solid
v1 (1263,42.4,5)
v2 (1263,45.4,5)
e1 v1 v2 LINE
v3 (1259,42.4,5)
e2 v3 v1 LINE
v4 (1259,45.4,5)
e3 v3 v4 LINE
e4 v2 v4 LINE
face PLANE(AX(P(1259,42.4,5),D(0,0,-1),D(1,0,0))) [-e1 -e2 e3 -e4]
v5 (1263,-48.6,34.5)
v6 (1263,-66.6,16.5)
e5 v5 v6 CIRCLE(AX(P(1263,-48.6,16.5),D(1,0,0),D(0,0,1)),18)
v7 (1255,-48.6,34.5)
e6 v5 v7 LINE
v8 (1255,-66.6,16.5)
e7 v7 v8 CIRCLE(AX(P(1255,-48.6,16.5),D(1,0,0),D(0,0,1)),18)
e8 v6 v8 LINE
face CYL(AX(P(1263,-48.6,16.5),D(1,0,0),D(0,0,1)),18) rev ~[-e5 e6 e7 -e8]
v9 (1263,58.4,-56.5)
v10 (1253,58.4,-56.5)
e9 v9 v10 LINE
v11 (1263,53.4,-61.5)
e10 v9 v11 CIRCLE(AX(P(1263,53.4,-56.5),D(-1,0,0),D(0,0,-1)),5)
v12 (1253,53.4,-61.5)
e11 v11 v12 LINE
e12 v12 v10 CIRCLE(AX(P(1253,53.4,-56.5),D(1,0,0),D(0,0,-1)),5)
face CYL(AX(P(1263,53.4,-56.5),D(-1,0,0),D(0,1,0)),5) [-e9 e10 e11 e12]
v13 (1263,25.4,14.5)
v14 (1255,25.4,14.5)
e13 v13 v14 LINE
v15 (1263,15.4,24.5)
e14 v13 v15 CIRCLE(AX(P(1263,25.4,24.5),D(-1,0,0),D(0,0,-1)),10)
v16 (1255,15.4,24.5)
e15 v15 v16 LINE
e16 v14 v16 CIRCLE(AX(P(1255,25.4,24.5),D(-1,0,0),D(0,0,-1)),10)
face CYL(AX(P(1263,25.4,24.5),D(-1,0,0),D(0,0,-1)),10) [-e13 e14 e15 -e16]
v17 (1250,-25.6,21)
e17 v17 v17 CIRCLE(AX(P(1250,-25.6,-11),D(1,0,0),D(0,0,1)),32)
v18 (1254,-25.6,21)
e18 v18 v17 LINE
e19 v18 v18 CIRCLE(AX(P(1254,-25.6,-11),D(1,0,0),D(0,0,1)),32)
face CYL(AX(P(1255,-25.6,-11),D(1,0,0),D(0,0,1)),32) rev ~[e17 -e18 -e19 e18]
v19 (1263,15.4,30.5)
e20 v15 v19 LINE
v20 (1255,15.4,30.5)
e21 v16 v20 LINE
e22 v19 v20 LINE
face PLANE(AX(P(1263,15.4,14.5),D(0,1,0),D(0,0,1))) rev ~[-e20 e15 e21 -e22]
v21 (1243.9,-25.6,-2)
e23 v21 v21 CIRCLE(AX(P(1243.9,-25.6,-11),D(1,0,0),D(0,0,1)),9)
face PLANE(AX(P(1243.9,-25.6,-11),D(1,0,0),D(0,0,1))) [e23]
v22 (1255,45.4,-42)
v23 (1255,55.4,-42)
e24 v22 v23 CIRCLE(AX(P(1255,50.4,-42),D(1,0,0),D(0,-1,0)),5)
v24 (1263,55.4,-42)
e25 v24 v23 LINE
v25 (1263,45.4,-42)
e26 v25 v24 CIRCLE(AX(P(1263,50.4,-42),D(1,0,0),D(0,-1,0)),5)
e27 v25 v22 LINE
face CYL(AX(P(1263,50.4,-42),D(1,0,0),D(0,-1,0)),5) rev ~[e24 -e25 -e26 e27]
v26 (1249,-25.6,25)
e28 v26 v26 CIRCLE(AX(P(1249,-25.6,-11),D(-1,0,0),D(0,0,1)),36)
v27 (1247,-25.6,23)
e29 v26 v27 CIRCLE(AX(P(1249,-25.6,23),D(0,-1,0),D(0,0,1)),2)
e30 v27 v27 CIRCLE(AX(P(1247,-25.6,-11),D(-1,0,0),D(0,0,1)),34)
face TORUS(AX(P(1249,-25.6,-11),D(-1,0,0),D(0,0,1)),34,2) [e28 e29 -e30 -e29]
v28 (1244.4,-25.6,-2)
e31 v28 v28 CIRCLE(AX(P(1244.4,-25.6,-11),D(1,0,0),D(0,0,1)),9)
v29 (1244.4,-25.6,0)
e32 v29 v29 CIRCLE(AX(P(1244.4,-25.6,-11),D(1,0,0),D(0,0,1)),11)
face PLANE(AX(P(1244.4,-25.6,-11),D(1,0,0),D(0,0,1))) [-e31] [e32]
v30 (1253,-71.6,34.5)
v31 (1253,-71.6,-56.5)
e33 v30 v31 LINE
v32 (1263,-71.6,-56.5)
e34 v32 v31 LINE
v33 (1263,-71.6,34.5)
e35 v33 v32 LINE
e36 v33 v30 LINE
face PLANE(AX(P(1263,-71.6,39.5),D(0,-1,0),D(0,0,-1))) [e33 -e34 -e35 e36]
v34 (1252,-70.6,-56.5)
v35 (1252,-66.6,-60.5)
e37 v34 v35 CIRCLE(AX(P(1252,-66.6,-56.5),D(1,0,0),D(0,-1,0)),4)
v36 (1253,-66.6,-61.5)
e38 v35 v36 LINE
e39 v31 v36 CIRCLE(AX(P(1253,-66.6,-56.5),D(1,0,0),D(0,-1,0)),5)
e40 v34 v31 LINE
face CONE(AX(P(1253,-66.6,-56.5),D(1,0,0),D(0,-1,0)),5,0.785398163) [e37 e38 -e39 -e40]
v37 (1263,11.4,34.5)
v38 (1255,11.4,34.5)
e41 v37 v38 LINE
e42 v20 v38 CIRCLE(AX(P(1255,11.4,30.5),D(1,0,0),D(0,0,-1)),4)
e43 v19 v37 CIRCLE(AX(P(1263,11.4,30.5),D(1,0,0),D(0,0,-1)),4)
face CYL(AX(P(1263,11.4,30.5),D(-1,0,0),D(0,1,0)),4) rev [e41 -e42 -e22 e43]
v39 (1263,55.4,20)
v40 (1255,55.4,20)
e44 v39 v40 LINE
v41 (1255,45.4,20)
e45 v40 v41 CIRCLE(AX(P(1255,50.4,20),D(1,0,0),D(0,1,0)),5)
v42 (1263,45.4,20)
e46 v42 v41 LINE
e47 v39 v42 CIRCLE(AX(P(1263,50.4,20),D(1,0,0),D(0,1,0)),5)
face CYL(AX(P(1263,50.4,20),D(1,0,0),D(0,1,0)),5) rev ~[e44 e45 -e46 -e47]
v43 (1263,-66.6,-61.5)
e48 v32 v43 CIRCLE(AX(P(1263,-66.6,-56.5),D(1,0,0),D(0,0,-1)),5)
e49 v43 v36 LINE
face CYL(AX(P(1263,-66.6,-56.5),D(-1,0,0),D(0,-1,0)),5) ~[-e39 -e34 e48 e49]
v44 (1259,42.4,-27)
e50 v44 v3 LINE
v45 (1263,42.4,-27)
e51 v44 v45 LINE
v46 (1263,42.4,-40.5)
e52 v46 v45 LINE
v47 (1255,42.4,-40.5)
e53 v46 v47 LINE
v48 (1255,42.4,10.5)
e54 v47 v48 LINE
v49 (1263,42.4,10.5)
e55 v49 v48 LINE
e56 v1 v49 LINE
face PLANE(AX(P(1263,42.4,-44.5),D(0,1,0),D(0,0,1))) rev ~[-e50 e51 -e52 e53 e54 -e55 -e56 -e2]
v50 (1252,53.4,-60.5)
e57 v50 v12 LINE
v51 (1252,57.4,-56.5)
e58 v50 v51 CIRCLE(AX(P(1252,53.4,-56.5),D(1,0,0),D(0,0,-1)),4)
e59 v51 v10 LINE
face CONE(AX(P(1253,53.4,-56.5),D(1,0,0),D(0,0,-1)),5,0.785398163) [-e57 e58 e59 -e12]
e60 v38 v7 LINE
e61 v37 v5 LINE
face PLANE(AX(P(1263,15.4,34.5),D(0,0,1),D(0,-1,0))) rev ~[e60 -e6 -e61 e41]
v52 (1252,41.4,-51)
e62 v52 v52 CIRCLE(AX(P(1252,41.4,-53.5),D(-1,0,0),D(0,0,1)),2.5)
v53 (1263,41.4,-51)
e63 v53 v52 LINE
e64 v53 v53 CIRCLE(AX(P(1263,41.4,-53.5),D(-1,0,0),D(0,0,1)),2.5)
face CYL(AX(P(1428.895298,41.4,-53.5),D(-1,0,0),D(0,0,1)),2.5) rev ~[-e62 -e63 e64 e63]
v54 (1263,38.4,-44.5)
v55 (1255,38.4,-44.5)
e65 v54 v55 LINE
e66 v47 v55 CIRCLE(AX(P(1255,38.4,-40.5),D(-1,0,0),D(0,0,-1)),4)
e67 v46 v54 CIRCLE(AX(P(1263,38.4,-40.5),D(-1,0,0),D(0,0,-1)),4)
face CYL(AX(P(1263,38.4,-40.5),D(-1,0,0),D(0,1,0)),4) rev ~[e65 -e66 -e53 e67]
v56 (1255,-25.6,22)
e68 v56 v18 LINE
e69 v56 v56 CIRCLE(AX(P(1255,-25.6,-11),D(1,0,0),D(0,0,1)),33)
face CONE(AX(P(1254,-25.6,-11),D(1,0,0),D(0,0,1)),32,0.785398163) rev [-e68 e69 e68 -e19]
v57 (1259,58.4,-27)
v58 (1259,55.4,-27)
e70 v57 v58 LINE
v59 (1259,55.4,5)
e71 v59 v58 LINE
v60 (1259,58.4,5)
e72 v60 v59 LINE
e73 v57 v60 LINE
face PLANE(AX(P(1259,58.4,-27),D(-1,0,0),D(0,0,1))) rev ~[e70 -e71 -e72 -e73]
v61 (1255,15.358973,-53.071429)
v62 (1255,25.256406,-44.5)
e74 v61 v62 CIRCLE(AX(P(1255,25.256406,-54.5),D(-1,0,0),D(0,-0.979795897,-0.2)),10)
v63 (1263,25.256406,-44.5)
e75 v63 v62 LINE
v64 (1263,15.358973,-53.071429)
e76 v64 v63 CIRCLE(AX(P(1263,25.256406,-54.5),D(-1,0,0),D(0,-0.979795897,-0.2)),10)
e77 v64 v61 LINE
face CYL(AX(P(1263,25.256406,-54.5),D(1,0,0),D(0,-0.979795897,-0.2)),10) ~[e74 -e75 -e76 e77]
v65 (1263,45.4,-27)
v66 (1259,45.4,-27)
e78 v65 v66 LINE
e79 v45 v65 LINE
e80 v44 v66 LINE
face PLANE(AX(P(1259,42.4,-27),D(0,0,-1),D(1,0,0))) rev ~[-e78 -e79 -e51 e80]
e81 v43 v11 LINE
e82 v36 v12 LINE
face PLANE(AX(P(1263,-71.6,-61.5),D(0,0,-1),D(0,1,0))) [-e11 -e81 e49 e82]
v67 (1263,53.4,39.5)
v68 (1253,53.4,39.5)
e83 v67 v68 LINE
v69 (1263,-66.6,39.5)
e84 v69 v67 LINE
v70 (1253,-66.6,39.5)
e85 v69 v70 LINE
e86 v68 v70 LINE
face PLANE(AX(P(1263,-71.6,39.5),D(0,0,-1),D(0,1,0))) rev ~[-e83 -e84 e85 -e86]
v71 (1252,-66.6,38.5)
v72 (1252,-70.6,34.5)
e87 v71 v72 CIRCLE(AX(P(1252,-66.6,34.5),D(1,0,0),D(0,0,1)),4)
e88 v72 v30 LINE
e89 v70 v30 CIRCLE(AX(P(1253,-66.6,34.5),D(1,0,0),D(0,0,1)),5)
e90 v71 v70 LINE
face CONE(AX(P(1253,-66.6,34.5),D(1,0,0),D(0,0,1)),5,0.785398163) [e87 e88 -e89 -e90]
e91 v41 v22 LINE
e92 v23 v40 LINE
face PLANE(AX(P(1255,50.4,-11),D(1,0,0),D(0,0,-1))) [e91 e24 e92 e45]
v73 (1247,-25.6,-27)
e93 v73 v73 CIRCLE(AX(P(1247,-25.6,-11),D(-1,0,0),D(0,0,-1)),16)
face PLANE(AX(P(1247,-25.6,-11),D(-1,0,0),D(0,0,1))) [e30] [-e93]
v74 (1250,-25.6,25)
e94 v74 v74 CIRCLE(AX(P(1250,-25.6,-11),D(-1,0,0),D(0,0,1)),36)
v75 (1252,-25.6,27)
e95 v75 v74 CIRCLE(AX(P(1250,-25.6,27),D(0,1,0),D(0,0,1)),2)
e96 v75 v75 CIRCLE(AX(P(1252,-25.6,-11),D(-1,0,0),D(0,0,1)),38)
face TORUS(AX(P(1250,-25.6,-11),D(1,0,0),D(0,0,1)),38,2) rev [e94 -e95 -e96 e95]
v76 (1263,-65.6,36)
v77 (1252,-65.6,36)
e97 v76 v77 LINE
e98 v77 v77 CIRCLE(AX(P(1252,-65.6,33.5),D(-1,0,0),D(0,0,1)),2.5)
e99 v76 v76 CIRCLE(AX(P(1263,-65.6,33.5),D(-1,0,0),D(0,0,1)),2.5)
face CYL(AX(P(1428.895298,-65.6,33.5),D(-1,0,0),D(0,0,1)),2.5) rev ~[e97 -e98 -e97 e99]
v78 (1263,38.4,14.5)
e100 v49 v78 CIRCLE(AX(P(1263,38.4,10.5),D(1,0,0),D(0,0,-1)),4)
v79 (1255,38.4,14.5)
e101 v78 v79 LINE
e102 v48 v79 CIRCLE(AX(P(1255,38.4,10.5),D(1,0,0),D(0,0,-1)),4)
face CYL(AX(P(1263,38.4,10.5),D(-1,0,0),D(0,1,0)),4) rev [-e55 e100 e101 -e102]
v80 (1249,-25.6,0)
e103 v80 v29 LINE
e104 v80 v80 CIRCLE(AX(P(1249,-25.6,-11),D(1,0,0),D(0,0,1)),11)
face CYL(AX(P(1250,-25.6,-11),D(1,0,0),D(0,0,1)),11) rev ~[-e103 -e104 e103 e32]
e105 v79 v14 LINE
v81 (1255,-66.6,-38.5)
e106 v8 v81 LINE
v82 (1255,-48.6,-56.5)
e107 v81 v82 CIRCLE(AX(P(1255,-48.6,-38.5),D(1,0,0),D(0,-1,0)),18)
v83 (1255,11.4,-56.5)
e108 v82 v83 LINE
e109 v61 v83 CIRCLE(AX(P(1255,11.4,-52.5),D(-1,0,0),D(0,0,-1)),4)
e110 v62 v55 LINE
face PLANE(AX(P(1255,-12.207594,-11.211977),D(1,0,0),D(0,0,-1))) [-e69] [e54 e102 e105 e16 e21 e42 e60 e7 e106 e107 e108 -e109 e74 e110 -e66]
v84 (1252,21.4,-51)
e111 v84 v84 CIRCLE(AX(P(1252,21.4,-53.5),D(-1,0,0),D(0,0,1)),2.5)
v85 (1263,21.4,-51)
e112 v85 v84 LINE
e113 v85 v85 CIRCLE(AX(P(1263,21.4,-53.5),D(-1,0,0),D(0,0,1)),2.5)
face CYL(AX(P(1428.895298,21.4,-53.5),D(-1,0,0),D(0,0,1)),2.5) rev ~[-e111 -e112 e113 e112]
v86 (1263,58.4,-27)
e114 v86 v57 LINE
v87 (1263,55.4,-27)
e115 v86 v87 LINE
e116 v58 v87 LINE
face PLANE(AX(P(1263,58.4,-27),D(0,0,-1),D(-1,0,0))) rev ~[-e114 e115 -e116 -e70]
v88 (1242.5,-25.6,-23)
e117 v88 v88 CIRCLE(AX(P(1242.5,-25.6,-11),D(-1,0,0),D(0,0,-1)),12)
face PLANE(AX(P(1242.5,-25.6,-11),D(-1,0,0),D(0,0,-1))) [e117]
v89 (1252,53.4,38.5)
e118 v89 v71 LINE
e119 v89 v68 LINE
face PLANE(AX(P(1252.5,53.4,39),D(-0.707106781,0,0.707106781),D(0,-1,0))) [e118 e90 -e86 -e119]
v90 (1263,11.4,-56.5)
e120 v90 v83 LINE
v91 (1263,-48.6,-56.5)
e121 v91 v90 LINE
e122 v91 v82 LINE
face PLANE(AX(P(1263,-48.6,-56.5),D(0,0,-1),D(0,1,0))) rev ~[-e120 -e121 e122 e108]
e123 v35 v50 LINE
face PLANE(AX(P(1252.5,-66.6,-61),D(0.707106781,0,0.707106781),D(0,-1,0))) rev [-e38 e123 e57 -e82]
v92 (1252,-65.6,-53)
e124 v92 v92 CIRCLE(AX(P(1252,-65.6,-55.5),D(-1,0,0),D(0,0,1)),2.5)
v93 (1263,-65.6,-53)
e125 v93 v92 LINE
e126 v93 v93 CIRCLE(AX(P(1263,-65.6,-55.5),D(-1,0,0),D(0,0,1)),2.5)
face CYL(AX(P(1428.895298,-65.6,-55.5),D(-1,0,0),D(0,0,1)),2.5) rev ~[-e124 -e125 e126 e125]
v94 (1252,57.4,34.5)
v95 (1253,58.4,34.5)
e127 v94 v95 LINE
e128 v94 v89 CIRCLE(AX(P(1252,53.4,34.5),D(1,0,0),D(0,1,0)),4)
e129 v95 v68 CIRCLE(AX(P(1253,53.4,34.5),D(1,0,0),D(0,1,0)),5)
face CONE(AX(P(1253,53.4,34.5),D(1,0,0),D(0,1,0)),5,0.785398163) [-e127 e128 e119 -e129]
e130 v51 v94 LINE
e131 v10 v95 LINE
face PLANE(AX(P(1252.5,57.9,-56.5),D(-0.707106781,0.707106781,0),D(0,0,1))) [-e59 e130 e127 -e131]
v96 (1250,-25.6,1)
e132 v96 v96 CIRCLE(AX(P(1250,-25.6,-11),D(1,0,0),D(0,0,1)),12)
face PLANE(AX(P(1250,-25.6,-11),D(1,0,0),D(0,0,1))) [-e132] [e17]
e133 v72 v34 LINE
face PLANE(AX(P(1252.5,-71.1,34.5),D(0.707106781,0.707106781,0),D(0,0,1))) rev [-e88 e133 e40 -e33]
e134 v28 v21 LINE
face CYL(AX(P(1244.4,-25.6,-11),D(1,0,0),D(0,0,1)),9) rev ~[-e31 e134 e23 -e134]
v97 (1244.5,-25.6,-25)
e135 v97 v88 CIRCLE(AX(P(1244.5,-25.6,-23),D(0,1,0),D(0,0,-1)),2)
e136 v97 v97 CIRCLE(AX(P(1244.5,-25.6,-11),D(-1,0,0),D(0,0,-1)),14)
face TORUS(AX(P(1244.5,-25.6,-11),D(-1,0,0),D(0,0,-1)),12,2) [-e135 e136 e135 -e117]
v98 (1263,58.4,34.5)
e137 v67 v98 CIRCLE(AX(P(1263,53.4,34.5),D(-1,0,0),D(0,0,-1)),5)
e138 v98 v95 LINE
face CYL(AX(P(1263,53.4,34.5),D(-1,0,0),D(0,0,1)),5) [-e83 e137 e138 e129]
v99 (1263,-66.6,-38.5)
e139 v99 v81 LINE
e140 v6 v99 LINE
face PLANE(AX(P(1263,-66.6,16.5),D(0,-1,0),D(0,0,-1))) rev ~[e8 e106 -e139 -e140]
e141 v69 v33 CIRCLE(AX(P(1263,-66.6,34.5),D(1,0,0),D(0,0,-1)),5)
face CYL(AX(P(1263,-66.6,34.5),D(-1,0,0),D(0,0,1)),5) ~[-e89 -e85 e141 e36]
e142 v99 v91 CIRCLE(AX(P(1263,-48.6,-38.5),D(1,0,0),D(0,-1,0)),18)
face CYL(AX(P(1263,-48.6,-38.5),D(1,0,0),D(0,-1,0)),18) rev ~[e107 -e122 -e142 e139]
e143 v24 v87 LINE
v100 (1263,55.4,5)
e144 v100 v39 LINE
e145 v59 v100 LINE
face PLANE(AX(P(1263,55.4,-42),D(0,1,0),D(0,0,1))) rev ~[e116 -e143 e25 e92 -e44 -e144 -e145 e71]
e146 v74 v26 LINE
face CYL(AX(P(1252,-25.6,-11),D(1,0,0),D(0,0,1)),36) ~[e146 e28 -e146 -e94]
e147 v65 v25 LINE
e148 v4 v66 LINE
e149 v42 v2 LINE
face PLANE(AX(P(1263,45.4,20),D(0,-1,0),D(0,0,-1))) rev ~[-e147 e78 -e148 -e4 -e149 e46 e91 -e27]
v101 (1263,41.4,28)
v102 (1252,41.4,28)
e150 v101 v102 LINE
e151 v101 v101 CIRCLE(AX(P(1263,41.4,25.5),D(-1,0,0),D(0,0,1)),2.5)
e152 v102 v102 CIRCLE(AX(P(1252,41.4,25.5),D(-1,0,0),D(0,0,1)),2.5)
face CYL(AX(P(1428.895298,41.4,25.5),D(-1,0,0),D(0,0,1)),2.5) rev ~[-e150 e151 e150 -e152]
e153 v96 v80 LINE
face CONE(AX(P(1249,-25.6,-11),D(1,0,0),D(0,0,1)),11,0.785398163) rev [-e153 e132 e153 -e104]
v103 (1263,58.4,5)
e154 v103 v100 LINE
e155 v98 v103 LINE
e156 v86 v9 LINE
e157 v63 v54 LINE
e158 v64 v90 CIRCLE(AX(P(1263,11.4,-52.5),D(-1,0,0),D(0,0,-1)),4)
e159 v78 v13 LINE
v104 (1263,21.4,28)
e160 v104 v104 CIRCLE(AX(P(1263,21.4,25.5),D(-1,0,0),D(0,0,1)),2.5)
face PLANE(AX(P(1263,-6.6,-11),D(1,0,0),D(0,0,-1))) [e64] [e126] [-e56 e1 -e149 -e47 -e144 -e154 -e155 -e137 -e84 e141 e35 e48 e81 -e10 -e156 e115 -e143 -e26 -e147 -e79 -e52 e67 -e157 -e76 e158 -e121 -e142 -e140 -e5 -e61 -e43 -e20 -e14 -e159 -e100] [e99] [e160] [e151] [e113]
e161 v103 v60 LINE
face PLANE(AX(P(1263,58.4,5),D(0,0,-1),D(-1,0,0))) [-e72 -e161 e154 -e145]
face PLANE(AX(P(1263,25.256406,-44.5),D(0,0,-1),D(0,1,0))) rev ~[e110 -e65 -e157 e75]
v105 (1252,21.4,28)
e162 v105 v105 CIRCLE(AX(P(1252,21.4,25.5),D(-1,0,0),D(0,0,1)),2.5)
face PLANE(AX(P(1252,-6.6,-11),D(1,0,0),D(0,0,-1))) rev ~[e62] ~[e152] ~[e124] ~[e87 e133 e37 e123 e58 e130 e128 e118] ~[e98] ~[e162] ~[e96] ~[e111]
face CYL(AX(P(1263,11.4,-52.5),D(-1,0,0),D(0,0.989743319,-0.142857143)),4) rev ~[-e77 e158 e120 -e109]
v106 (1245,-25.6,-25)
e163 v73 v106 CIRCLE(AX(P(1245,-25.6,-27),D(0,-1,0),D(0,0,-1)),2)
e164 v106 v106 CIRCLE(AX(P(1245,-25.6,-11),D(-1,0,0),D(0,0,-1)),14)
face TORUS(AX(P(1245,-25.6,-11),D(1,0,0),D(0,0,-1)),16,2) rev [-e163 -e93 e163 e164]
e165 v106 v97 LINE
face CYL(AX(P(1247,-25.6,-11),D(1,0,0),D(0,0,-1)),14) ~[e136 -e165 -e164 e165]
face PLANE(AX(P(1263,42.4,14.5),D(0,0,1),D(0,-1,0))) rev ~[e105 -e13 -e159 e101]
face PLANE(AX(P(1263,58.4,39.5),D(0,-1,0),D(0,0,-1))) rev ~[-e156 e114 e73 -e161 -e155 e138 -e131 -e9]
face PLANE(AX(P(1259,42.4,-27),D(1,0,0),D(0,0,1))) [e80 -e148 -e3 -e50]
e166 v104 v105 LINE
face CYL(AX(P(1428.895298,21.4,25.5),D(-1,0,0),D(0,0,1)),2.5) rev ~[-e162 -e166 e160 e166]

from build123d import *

# Parameters (mm, degrees)
SKETCH_1_W          = 101
SKETCH_1_H          = 130
EXTRUDE_1_DEPTH     = 11
CUT_EXTRUDE_1_DEPTH = 8
CUT_EXTRUDE_2_DEPTH = 8
CUT_EXTRUDE_3_REACH = 1271.625
SKETCH_4_W          = 4
SKETCH_4_H          = 32
CUT_EXTRUDE_4_REACH = 1273.161
SKETCH_5_W          = 4
SKETCH_5_H          = 32
SKETCH_6_R          = 36
EXTRUDE_2_DEPTH     = 5
SKETCH_7_R          = 14
EXTRUDE_3_DEPTH     = 4.5
SKETCH_8_R          = 32
CUT_EXTRUDE_5_DEPTH = 5
SKETCH_9_R          = 11
CUT_EXTRUDE_6_DEPTH = 5.6
SKETCH_10_R         = 9
CUT_EXTRUDE_7_DEPTH = 0.5
HOLE_WIZARD_M6_1_D  = 5
FILLET_1_R          = 5
CHAMFER_1_SIZE      = 1
FILLET_2_R          = 2
FILLET_3_R          = 4
FILLET_4_R          = 10


with BuildPart() as part:
    # 草图1 → 凸台-拉伸1 (new body)
    with BuildSketch(Plane(origin=(1263, 0, 0), x_dir=(0, 0, -1), z_dir=(1, 0, 0))):
        with Locations((11, -6.6)):
            Rectangle(SKETCH_1_W, SKETCH_1_H)
    extrude(amount=-EXTRUDE_1_DEPTH)

    # 草图2 → 切除-拉伸1 (cut)
    with BuildSketch(Plane(origin=(1263, 0, 0), x_dir=(0, 0, -1), z_dir=(1, 0, 0))):
        with BuildLine():
            Line((44.5, 25.256406461), (44.5, 42.4))
            Line((44.5, 42.4), (-14.5, 42.4))
            Line((-14.5, 42.4), (-14.5, 15.4))
            Line((-14.5, 15.4), (-34.5, 15.4))
            Line((-34.5, 15.4), (-34.5, -48.6))
            ThreePointArc((-34.5, -48.6), (-29.227922061, -61.327922061), (-16.5, -66.6))
            Line((-16.5, -66.6), (38.5, -66.6))
            ThreePointArc((38.5, -66.6), (51.227922061, -61.327922061), (56.5, -48.6))
            Line((56.5, -48.6), (56.5, 15.458447489))
            ThreePointArc((56.5, 15.458447489), (48.17544468, 17.510439768), (44.5, 25.256406461))
        make_face()
    extrude(amount=-CUT_EXTRUDE_1_DEPTH, mode=Mode.SUBTRACT)

    # 草图3 → 切除-拉伸2 (cut)
    with BuildSketch(Plane(origin=(1263, 0, 0), x_dir=(0, 0, -1), z_dir=(1, 0, 0))):
        with BuildLine():
            Line((42, 55.4), (-20, 55.4))
            ThreePointArc((-20, 55.4), (-25, 50.4), (-20, 45.4))
            Line((-20, 45.4), (42, 45.4))
            ThreePointArc((42, 45.4), (47, 50.4), (42, 55.4))
        make_face()
    extrude(amount=-CUT_EXTRUDE_2_DEPTH, mode=Mode.SUBTRACT)

    # 草图4 → 切除-拉伸3 (cut, up to next)
    with BuildSketch(Plane.XZ.offset(-42.4), mode=Mode.PRIVATE) as cut_extrude_3_sk1:
        with Locations((1261, -11)):
            Rectangle(SKETCH_4_W, SKETCH_4_H)
    cut_extrude_3_tool1 = extrude(cut_extrude_3_sk1.sketch, amount=-CUT_EXTRUDE_3_REACH, mode=Mode.PRIVATE) & part.part
    add(cut_extrude_3_tool1.solids().sort_by_distance((1261, 42.4, -11))[0], mode=Mode.SUBTRACT)

    # 草图5 → 切除-拉伸4 (cut, up to next)
    with BuildSketch(Plane(origin=(0, 58.4, 0), x_dir=(-1, 0, 0), z_dir=(0, 1, 0)), mode=Mode.PRIVATE) as cut_extrude_4_sk1:
        with Locations((-1261, -11)):
            Rectangle(SKETCH_5_W, SKETCH_5_H)
    cut_extrude_4_tool1 = extrude(cut_extrude_4_sk1.sketch, amount=-CUT_EXTRUDE_4_REACH, mode=Mode.PRIVATE) & part.part
    add(cut_extrude_4_tool1.solids().sort_by_distance((1261, 58.4, -11))[0], mode=Mode.SUBTRACT)

    # 草图6 → 凸台-拉伸2 (add)
    with BuildSketch(Plane.ZY.offset(-1252)):
        with Locations((-11, -25.6)):
            Circle(SKETCH_6_R)
    extrude(amount=EXTRUDE_2_DEPTH)

    # 草图7 → 凸台-拉伸3 (add)
    with BuildSketch(Plane.ZY.offset(-1247)):
        with Locations(Location((-11, -25.6, 0), (0, 0, 180))):
            Circle(SKETCH_7_R)
    extrude(amount=EXTRUDE_3_DEPTH)

    # 草图8 → 切除-拉伸5 (cut)
    with BuildSketch(Plane(origin=(1255, 0, 0), x_dir=(0, 0, -1), z_dir=(1, 0, 0))):
        with Locations(Location((11, -25.6, 0), (0, 0, 180))):
            Circle(SKETCH_8_R)
    extrude(amount=-CUT_EXTRUDE_5_DEPTH, mode=Mode.SUBTRACT)

    # 草图9 → 切除-拉伸6 (cut)
    with BuildSketch(Plane(origin=(1250, 0, 0), x_dir=(0, 0, -1), z_dir=(1, 0, 0))):
        with Locations(Location((11, -25.6, 0), (0, 0, 180))):
            Circle(SKETCH_9_R)
    extrude(amount=-CUT_EXTRUDE_6_DEPTH, mode=Mode.SUBTRACT)

    # 草图10 → 切除-拉伸7 (cut)
    with BuildSketch(Plane(origin=(1244.4, 0, 0), x_dir=(0, 0, -1), z_dir=(1, 0, 0))):
        with Locations(Location((11, -25.6, 0), (0, 0, 180))):
            Circle(SKETCH_10_R)
    extrude(amount=-CUT_EXTRUDE_7_DEPTH, mode=Mode.SUBTRACT)

    # M6 螺纹孔1 (through all)
    with Locations(Plane(origin=(1263, 0, 0), x_dir=(0, 0, -1), z_dir=(1, 0, 0))):
        with Locations((53.5, 41.4), (-25.5, 41.4), (-25.5, 21.4), (-33.5, -65.6), (55.5, -65.6), (53.5, 21.4)):
            Hole(HOLE_WIZARD_M6_1_D / 2)

    # 圆角1
    fillet_1_edges = [part.edges().sort_by_distance(p)[0] for p in [
        (1257.5, -71.6, 39.5),
        (1257.5, 58.4, 39.5),
        (1257.5, 58.4, -61.5),
        (1257.5, -71.6, -61.5),
    ]]
    fillet(fillet_1_edges, radius=FILLET_1_R)

    # 倒角1
    chamfer_1_edges = [part.edges().sort_by_distance(p)[0] for p in [
        (1252, -6.6, -61.5),
        (1252, 58.4, -11),
        (1252, -71.6, -11),
        (1252, -6.6, 39.5),
        (1252, -70.135533906, 38.035533906),
        (1252, 56.935533906, 38.035533906),
        (1252, -70.135533906, -60.035533906),
        (1252, 56.935533906, -60.035533906),
        (1255, -25.6, -43),
        (1250, -25.6, -22),
    ]]
    chamfer(chamfer_1_edges, length=CHAMFER_1_SIZE)

    # 圆角2
    fillet_2_edges = [part.edges().sort_by_distance(p)[0] for p in [
        (1252, -25.6, -47),
        (1247, -25.6, -47),
        (1247, -25.6, 3),
        (1242.5, -25.6, 3),
    ]]
    fillet(fillet_2_edges, radius=FILLET_2_R)

    # 圆角3
    fillet_3_edges = [part.edges().sort_by_distance(p)[0] for p in [
        (1259, 15.458447489, -56.5),
        (1259, 15.4, 34.5),
        (1259, 42.4, 14.5),
        (1259, 42.4, -44.5),
    ]]
    fillet(fillet_3_edges, radius=FILLET_3_R)

    # 圆角4
    fillet_4_edges = [part.edges().sort_by_distance(p)[0] for p in [
        (1259, 15.4, 14.5),
    ]]
    fillet(fillet_4_edges, radius=FILLET_4_R)


solid = part.part
